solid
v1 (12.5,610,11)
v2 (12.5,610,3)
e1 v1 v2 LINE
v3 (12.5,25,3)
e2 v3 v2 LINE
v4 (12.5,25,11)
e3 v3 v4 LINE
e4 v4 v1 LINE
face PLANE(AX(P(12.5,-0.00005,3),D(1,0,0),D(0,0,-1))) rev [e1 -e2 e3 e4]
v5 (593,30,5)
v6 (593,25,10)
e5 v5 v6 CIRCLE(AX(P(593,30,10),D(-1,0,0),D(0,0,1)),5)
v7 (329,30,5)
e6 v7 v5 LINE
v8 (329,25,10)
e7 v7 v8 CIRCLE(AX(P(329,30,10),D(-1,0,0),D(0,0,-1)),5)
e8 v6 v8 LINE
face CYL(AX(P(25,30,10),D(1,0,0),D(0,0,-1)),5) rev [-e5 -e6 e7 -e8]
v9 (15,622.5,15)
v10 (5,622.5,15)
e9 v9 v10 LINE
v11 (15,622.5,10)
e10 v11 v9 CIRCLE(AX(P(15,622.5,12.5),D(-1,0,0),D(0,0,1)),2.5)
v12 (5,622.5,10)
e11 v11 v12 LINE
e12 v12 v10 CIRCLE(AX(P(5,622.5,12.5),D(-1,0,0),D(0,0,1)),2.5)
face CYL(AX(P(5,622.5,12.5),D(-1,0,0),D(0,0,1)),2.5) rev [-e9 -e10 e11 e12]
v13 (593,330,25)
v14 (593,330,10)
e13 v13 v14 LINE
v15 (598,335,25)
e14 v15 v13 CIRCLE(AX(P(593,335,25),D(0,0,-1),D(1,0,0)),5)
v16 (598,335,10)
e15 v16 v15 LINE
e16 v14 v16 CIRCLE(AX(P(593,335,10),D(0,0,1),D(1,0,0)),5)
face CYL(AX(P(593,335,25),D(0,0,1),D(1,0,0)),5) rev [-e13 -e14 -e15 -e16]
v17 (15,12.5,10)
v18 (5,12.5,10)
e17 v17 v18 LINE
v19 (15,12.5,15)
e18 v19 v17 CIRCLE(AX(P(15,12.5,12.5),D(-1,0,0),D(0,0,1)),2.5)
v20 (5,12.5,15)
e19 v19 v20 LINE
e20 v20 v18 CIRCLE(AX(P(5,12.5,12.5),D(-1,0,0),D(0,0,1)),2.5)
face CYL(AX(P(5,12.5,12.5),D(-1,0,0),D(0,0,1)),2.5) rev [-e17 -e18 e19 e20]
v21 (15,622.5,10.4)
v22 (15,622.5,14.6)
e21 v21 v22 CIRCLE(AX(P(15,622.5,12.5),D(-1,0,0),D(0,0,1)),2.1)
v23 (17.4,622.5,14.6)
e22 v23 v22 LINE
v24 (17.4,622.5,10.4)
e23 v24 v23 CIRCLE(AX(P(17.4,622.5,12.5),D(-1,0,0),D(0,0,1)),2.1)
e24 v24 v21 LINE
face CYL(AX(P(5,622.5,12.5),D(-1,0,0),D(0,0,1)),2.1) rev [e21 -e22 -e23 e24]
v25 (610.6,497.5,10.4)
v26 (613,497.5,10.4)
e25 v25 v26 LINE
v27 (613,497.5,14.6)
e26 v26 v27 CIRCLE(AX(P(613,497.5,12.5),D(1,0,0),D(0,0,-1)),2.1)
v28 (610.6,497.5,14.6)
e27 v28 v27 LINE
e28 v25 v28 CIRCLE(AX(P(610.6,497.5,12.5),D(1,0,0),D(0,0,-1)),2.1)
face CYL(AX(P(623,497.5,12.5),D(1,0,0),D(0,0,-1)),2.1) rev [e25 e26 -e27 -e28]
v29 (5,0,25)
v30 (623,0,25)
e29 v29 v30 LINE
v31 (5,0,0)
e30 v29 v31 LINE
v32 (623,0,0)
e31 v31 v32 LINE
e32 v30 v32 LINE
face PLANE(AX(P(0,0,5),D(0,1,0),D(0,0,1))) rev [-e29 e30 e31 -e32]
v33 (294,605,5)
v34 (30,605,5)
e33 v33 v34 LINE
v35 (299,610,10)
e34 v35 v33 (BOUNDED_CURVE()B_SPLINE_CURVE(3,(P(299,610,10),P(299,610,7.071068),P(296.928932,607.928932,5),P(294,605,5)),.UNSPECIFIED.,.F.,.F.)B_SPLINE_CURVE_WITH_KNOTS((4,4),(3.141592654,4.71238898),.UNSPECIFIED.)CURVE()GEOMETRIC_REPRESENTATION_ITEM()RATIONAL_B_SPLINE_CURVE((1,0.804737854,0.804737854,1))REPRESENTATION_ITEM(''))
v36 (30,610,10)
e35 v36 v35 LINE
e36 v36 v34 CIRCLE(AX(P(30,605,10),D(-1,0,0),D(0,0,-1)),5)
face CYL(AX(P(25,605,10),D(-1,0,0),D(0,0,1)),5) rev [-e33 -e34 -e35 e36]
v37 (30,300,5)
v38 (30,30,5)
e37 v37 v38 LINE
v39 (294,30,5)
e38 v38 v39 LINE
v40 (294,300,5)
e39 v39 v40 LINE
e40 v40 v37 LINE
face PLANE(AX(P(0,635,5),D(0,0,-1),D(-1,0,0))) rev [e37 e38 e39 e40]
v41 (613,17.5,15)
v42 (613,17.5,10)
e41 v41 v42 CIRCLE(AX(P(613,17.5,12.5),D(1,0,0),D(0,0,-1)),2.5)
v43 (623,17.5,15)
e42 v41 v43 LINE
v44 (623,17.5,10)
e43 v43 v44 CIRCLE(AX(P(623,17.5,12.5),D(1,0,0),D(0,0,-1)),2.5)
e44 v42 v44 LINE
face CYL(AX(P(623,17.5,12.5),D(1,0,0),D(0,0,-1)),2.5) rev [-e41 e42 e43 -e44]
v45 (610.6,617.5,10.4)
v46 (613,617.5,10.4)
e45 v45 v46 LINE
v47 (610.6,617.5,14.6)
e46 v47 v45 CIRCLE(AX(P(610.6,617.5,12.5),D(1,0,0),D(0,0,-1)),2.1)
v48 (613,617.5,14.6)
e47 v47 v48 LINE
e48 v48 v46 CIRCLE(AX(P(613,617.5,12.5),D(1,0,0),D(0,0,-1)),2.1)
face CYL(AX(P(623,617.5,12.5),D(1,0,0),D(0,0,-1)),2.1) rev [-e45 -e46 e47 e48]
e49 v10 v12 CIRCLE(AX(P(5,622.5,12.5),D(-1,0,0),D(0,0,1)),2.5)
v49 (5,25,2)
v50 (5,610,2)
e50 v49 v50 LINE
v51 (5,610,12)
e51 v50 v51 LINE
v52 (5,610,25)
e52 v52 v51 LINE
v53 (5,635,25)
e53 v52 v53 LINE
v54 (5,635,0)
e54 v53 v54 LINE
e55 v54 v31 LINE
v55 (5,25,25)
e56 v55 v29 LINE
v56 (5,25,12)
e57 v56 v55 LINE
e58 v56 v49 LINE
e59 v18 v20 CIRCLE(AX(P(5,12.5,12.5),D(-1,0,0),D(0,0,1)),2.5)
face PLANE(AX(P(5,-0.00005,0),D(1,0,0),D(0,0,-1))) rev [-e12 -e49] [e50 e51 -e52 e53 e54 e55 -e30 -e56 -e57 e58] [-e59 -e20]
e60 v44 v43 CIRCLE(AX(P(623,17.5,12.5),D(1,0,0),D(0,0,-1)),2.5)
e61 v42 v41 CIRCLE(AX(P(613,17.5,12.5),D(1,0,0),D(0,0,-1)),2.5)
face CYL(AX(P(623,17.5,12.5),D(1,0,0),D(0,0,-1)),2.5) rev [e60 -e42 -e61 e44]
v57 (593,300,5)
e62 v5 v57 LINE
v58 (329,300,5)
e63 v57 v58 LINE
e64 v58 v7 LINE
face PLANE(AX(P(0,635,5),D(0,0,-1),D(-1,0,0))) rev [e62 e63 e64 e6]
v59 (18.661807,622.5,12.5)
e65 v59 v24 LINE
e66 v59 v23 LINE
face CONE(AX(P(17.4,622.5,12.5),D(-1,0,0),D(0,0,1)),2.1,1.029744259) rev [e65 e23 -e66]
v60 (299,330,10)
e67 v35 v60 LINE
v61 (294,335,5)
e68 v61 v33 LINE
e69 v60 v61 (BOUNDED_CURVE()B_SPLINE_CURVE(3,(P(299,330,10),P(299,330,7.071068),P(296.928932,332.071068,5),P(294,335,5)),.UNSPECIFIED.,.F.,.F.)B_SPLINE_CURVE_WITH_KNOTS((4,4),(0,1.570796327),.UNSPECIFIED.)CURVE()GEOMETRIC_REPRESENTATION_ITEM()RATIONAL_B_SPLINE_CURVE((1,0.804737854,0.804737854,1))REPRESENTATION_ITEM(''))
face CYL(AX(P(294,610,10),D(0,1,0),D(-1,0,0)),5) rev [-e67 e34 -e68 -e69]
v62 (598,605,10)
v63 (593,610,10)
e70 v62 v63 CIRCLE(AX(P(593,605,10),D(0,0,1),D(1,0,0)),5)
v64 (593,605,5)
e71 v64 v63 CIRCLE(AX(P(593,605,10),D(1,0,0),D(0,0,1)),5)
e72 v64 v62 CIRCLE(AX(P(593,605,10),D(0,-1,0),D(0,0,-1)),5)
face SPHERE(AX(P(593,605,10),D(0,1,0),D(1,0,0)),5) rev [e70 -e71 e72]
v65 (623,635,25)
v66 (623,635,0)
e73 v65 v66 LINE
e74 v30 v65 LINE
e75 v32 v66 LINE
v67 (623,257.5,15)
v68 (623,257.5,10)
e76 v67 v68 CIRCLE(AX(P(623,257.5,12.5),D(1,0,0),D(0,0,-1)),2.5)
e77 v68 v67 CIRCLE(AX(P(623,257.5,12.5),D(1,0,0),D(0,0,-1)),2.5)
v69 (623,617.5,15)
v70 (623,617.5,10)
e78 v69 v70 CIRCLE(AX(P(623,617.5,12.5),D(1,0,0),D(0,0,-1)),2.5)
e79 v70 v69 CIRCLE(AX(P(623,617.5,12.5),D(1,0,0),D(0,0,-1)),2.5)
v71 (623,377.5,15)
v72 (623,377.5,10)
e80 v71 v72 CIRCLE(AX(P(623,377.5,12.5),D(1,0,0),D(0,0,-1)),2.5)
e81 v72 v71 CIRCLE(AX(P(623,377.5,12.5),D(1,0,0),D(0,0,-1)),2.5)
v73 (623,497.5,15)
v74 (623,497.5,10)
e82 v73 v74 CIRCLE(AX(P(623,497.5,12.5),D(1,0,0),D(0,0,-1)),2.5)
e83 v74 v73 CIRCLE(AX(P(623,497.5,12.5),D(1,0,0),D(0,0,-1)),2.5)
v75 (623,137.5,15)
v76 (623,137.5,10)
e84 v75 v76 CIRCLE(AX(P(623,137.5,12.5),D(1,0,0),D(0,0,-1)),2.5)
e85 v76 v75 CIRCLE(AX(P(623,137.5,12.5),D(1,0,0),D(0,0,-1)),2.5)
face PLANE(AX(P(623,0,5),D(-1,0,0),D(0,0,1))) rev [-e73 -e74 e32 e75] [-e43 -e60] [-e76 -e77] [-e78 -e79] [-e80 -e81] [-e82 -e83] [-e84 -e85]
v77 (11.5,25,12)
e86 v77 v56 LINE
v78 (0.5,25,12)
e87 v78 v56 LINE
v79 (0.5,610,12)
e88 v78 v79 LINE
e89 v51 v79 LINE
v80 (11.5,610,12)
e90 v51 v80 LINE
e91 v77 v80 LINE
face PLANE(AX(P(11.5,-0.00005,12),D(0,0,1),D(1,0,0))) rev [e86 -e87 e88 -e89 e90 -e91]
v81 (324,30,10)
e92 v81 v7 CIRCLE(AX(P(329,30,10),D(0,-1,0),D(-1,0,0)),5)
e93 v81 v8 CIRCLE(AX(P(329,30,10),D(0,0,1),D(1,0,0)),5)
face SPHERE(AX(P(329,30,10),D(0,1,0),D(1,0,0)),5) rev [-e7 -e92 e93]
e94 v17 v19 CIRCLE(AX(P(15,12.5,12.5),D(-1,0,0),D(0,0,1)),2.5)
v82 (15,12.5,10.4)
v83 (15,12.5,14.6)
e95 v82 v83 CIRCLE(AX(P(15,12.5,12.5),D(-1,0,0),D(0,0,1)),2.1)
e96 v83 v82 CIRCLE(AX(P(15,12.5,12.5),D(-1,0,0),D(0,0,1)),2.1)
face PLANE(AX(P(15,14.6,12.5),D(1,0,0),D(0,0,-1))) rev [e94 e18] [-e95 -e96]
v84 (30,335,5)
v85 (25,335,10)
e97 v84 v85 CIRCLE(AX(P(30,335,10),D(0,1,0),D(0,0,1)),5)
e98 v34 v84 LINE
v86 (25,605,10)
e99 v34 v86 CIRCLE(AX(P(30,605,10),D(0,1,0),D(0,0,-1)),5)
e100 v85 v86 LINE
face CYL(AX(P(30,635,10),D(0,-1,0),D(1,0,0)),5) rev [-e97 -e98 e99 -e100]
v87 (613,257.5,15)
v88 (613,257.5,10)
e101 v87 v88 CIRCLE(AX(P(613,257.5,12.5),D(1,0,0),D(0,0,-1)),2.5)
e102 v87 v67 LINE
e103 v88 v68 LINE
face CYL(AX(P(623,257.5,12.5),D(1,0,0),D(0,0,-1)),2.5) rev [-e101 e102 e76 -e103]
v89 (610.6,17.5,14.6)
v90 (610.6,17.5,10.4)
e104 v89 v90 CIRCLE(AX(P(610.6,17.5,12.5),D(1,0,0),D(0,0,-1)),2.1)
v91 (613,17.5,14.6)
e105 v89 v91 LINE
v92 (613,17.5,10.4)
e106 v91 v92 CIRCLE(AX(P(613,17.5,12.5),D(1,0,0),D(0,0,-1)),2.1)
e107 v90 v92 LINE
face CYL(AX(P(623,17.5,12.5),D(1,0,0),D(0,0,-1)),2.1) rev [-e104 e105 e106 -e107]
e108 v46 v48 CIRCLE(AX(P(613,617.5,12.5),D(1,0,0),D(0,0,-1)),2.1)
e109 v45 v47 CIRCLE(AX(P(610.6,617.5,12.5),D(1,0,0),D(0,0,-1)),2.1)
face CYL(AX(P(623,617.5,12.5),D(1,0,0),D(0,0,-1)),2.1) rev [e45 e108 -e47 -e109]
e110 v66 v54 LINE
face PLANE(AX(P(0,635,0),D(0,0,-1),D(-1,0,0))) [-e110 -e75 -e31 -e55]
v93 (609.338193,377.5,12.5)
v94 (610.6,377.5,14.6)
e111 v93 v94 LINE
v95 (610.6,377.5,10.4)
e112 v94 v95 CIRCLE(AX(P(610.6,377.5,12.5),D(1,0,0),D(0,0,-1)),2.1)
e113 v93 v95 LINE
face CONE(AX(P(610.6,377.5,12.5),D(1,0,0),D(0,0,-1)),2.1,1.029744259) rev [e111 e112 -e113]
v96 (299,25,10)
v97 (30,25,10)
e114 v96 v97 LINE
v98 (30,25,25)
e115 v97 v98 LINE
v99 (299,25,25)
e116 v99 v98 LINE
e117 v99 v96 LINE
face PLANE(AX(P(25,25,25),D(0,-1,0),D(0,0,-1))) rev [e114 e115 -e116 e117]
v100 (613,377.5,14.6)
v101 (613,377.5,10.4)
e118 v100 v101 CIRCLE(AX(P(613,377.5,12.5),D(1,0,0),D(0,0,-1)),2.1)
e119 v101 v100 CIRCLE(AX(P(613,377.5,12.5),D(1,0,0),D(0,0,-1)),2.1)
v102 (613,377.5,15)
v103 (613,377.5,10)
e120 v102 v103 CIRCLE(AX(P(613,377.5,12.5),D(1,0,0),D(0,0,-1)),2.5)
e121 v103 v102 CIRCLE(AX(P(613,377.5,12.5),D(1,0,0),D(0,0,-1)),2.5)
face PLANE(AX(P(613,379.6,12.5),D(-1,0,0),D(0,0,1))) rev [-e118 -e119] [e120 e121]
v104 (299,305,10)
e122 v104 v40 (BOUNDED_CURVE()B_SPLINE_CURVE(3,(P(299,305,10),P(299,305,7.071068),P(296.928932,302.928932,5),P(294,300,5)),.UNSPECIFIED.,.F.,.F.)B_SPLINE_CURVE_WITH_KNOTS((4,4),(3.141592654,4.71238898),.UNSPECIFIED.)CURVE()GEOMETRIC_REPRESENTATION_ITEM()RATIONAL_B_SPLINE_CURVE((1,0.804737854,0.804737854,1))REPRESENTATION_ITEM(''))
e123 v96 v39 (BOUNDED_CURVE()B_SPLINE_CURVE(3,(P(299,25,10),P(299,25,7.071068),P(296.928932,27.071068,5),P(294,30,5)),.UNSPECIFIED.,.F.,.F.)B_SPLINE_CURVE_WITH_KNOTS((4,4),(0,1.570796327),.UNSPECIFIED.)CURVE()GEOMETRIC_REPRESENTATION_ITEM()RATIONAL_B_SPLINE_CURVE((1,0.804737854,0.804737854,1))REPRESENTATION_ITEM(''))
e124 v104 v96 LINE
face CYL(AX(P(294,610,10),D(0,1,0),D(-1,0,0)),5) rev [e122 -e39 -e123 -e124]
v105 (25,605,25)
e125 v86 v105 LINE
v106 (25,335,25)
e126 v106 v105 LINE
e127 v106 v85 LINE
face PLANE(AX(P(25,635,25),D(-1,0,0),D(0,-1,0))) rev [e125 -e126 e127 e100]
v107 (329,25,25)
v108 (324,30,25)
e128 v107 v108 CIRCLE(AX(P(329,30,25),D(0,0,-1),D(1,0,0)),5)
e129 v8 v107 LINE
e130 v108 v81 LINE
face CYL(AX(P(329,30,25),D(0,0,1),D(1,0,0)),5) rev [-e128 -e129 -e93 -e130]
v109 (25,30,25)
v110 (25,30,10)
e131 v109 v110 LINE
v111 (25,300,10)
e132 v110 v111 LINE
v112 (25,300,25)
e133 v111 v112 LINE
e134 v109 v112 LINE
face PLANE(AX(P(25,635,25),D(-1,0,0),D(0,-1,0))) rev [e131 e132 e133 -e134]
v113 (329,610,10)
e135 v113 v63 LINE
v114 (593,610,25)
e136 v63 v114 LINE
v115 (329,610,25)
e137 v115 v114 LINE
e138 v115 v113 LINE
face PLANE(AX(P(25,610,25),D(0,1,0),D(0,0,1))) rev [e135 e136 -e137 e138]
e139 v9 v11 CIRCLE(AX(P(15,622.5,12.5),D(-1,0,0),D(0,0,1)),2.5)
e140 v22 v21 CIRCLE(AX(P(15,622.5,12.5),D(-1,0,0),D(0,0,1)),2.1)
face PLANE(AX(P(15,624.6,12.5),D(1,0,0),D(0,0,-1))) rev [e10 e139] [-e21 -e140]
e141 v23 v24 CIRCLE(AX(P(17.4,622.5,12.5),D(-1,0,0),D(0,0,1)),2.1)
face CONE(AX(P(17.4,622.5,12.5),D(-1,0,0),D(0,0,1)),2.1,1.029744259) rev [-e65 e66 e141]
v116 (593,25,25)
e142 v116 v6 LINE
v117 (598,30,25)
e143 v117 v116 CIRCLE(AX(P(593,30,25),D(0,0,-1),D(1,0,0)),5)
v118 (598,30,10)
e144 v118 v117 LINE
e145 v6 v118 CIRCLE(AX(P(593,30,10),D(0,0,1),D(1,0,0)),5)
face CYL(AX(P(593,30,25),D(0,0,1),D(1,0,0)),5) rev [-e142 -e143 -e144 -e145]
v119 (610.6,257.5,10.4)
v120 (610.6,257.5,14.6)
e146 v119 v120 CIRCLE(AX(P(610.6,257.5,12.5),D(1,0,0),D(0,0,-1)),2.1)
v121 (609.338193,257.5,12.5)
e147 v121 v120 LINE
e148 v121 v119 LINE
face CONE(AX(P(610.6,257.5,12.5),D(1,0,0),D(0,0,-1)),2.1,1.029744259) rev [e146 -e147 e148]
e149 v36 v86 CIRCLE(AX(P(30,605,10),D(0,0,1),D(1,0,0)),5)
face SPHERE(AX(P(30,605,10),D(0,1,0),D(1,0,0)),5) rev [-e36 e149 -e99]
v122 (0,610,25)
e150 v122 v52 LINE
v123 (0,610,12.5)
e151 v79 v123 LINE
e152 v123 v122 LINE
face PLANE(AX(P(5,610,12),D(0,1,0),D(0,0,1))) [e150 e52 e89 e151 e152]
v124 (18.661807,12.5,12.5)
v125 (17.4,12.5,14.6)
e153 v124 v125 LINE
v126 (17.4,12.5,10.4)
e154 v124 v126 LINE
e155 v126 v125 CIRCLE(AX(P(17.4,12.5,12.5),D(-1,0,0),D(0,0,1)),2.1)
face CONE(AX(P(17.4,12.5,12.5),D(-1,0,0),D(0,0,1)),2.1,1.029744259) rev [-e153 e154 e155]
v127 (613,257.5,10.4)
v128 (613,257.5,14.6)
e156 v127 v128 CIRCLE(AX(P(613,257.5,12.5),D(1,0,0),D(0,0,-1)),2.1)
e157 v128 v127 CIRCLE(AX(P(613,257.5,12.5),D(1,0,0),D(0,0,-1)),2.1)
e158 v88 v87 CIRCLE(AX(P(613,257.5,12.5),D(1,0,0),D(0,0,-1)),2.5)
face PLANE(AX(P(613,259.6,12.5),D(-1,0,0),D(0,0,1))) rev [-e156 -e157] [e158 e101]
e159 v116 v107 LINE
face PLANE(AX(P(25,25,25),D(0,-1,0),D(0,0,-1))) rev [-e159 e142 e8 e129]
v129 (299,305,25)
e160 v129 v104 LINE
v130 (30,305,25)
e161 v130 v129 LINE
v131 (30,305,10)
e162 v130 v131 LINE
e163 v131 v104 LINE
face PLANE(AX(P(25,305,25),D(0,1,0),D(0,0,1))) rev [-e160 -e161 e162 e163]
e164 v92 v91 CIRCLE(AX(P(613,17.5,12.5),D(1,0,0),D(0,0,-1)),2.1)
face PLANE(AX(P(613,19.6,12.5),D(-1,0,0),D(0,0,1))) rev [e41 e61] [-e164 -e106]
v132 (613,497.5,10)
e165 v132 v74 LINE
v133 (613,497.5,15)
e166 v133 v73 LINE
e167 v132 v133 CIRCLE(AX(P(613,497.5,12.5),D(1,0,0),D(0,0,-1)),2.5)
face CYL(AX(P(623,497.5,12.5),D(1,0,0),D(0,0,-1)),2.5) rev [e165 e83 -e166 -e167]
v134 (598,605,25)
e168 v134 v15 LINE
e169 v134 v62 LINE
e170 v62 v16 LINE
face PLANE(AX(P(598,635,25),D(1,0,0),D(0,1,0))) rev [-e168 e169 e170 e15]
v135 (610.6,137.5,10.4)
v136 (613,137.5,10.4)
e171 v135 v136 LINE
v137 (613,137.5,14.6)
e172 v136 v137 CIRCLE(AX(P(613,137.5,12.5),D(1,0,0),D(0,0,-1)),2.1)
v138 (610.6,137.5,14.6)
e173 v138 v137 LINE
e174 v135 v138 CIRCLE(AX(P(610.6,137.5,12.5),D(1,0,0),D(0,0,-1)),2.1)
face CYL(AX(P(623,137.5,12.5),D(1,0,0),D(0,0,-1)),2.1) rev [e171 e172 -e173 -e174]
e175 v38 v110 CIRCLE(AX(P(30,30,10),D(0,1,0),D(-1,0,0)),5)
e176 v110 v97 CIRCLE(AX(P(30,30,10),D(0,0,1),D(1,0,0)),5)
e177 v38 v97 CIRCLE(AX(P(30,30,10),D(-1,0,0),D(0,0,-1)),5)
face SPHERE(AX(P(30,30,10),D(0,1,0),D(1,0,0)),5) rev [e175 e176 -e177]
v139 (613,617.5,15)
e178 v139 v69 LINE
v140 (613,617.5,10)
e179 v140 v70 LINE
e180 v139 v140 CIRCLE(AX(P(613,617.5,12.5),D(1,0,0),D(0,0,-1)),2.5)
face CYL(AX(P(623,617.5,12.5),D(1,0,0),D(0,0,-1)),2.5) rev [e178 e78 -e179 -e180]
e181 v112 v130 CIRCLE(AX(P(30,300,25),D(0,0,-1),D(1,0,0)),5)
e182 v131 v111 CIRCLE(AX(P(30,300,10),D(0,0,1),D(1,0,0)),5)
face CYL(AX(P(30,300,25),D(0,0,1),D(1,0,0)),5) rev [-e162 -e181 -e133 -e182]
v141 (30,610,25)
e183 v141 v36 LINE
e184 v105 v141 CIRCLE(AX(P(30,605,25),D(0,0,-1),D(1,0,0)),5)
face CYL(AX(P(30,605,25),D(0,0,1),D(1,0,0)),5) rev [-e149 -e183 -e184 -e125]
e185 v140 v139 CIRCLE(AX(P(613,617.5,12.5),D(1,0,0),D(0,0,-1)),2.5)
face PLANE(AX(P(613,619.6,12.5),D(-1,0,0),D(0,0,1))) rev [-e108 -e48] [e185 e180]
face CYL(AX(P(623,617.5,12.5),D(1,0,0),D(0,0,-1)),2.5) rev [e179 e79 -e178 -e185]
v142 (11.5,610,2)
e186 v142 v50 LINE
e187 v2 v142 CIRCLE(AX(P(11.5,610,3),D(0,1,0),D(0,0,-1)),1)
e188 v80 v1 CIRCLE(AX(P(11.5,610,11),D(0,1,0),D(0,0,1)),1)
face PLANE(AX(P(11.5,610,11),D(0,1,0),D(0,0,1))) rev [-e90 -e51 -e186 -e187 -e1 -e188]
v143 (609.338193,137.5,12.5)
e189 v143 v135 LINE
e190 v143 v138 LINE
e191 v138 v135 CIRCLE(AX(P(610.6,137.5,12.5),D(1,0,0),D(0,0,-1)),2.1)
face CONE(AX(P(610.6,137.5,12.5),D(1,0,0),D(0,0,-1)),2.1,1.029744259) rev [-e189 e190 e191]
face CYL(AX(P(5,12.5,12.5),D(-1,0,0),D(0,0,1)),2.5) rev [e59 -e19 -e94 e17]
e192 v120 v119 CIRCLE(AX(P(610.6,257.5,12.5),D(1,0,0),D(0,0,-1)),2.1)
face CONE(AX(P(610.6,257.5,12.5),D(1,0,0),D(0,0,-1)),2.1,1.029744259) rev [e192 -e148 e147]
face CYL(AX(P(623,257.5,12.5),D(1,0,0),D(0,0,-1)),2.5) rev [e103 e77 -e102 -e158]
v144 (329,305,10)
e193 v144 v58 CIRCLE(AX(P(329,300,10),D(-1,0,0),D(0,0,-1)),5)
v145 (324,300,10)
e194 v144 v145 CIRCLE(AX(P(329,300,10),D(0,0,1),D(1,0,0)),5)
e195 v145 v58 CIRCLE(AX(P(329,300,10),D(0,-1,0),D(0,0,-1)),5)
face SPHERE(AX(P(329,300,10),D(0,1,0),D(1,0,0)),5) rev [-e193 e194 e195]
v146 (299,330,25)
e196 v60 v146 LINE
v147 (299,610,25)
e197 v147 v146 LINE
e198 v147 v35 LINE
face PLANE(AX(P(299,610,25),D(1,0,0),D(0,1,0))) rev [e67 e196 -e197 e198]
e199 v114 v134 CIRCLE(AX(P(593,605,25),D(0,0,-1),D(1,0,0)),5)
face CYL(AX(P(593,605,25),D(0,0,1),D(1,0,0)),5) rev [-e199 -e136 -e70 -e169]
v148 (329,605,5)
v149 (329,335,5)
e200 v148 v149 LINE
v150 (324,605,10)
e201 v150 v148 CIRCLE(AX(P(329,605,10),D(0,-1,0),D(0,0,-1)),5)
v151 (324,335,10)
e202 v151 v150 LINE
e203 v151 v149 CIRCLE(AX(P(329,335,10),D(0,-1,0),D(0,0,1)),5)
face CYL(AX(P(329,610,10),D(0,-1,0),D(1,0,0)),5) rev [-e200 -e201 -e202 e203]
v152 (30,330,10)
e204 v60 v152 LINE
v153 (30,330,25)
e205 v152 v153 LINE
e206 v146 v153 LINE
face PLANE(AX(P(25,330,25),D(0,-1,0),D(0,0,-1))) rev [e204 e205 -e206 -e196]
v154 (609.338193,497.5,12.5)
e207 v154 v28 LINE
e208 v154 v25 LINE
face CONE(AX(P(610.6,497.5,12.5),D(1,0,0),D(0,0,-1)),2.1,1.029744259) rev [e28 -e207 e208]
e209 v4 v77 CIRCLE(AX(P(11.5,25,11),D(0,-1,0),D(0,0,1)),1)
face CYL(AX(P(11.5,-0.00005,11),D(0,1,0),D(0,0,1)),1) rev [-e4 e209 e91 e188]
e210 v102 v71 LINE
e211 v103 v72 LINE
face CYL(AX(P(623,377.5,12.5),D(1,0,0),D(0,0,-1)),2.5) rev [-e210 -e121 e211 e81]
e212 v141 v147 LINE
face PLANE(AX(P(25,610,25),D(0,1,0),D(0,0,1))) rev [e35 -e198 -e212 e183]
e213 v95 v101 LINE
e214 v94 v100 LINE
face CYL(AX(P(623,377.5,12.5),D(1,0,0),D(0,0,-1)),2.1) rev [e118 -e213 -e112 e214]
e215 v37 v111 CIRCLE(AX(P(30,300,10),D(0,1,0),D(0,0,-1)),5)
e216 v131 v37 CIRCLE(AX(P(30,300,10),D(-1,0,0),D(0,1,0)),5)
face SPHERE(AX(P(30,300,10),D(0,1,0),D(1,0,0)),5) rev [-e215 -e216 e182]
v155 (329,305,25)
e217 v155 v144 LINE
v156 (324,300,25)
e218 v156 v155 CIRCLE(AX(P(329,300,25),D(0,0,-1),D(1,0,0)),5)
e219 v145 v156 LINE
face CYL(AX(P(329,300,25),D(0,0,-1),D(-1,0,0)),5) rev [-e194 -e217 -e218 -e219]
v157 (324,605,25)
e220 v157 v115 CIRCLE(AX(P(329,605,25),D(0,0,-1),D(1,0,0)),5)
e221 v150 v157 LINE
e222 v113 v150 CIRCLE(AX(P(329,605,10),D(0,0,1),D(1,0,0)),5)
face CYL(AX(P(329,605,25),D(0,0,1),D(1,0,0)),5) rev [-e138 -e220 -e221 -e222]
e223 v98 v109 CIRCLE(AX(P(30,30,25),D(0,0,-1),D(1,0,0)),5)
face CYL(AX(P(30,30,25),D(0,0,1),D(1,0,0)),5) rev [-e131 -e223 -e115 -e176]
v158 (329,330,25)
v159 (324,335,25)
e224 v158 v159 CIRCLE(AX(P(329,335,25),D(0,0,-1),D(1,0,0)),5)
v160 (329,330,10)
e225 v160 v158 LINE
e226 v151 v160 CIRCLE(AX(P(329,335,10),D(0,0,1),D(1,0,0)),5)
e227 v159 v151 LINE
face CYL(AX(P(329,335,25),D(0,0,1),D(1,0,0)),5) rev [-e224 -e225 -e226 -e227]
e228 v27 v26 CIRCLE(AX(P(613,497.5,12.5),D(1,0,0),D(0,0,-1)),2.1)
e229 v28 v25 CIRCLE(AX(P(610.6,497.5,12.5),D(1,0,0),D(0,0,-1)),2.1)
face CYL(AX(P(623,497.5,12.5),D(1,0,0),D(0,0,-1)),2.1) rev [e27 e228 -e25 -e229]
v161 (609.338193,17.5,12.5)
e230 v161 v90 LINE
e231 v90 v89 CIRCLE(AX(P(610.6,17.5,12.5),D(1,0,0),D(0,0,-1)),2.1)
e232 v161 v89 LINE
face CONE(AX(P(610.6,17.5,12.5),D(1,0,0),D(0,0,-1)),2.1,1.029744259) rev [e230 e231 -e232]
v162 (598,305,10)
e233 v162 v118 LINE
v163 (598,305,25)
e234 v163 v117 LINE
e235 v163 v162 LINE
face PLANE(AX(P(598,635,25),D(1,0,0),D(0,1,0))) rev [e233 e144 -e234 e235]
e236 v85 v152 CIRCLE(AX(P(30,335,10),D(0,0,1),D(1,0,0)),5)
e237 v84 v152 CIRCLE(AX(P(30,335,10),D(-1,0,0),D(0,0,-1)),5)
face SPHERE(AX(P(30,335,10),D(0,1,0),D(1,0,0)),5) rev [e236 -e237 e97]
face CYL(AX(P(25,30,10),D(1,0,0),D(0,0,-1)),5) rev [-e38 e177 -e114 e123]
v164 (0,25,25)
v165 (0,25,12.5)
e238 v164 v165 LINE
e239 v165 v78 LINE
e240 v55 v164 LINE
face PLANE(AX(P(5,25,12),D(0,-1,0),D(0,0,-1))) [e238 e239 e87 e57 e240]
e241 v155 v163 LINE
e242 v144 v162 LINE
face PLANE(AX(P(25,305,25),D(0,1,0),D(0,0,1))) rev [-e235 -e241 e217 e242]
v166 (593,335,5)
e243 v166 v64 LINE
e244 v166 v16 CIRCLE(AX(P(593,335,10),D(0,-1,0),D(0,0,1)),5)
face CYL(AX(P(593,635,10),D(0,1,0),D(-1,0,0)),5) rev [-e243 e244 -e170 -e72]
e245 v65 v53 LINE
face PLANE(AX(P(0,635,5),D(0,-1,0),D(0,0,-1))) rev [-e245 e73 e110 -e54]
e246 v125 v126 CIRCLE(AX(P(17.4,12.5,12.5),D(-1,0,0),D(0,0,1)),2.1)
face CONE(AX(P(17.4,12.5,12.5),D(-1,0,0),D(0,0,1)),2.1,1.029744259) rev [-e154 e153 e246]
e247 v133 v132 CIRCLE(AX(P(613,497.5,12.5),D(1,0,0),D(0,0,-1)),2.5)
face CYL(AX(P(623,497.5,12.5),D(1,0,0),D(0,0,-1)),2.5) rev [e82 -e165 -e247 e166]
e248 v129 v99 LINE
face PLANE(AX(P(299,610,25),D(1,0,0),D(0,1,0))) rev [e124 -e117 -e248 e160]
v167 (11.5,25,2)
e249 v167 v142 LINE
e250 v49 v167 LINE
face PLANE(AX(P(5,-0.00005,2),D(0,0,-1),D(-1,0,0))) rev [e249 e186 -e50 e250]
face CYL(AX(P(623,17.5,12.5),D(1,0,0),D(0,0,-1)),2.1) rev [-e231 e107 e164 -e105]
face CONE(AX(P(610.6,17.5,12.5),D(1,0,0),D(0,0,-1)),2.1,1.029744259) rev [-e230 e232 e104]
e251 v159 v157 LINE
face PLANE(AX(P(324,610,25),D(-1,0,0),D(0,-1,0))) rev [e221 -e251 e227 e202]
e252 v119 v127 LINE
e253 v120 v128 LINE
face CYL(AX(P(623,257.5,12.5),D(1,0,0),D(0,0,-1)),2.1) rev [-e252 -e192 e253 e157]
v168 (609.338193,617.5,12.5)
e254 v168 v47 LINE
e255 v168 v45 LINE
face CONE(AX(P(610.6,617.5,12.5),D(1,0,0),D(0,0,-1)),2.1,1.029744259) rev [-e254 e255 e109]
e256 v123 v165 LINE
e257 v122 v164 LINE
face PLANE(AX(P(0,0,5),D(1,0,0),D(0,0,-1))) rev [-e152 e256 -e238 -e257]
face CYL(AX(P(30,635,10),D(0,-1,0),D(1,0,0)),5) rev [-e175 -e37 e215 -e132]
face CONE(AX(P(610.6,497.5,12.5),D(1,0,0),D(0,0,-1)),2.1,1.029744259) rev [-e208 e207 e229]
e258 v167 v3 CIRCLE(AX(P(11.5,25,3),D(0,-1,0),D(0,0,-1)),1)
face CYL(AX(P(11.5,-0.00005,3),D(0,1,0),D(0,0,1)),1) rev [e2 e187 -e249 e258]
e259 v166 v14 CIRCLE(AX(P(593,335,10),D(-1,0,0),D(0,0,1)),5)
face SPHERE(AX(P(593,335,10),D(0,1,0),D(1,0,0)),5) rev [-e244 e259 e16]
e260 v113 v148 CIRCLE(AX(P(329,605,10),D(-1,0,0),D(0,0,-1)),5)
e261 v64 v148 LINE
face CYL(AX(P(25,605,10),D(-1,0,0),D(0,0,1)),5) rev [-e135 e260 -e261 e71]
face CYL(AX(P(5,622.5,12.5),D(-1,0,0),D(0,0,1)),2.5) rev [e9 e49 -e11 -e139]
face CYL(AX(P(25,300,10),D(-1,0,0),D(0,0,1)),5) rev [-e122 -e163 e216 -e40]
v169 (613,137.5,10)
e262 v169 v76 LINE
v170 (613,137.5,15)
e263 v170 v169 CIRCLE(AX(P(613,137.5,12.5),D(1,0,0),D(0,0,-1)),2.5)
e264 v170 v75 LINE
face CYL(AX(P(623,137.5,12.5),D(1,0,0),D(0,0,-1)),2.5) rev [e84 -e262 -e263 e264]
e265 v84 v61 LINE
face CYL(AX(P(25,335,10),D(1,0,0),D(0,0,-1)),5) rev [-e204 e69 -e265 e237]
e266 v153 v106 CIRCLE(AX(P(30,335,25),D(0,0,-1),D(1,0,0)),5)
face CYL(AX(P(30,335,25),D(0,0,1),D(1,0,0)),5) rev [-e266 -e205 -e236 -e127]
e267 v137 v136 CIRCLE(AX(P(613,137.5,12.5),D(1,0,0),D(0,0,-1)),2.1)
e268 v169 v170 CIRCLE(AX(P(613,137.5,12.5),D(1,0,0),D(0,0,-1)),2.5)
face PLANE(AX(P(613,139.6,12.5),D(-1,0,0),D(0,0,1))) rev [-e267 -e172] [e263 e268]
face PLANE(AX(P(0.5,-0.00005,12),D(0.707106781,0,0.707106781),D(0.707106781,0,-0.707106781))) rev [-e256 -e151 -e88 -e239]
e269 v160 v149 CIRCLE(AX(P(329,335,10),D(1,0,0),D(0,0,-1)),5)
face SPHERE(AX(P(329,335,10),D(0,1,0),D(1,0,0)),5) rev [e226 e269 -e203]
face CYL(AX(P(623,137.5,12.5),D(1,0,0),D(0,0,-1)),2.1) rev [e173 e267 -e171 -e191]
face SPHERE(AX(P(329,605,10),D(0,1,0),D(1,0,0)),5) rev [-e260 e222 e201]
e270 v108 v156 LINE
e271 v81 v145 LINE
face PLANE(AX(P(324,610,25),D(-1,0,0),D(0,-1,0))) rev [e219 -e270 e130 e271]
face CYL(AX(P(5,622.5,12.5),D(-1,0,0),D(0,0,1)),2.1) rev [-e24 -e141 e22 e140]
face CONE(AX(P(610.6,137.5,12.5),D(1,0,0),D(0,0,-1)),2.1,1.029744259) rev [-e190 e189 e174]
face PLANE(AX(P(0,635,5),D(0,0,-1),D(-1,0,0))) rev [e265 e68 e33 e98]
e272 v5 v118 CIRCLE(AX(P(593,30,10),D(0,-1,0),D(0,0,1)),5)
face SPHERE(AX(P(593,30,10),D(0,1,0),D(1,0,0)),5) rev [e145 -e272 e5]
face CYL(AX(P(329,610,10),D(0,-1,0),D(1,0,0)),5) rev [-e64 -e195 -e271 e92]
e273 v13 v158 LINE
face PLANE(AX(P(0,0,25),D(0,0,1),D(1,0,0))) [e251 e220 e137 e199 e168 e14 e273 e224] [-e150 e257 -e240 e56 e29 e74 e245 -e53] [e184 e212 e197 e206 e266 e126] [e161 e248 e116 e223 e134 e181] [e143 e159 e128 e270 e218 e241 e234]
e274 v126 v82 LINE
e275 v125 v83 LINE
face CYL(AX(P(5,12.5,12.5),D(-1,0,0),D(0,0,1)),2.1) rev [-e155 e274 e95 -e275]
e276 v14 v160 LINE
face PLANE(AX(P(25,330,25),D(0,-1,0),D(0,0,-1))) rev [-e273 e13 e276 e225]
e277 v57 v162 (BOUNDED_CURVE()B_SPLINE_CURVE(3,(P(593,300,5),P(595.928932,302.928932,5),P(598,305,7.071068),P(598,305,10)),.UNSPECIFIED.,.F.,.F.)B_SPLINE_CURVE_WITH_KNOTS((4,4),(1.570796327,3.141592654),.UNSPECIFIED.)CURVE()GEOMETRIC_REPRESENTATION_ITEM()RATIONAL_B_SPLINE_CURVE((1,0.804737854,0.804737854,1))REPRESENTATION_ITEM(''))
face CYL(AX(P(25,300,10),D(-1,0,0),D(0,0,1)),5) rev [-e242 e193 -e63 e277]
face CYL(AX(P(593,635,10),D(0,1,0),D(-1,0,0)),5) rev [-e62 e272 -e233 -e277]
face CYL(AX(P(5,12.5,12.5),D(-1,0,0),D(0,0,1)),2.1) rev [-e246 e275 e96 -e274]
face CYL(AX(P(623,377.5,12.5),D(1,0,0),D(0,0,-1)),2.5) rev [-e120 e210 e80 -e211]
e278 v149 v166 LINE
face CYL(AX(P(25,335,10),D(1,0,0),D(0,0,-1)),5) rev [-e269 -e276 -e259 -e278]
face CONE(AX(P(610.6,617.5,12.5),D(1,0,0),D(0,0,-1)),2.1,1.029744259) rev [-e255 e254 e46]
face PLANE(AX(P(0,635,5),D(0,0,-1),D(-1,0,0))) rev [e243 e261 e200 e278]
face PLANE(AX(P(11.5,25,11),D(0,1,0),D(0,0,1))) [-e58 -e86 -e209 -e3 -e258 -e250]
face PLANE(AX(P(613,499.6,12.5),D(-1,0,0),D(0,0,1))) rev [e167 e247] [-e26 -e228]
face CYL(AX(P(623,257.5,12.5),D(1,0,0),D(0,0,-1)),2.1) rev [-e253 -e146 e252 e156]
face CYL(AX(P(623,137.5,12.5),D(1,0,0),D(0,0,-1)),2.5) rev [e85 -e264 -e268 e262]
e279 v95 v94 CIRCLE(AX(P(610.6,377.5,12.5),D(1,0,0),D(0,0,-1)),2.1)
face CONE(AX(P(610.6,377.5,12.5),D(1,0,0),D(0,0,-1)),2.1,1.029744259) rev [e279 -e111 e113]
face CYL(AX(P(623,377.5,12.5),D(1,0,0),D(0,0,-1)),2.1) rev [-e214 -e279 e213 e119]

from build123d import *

# Parameters (mm, degrees)
SKETCH_1_W           = 623
SKETCH_1_H           = 635
EXTRUDE_1_DEPTH      = 5
SKETCH_2_W           = 25
SKETCH_2_H           = 635
EXTRUDE_2_DEPTH      = 20
SKETCH_3_W           = 25
SKETCH_3_H           = 635
EXTRUDE_3_DEPTH      = 20
CUT_EXTRUDE_1_DEPTH  = 890.932019876
CHAMFER_1_SIZE       = 0.5
SKETCH_7_W           = 573
SKETCH_7_H           = 25
EXTRUDE_4_DEPTH      = 20
SKETCH_8_W           = 573
SKETCH_8_H           = 25
EXTRUDE_5_DEPTH      = 20
SKETCH_9_W           = 573
SKETCH_9_H           = 25
EXTRUDE_6_DEPTH      = 20
SKETCH_10_W          = 25
SKETCH_10_H          = 585
EXTRUDE_7_DEPTH      = 20
EXTRUDE_8_DEPTH      = 25
CUT_EXTRUDE_2_DEPTH  = 25
EXTRUDE_START        = -25
EXTRUDE_9_DEPTH      = 25
CUT_EXTRUDE_3_DEPTH  = 25
M5X0_8_1_D           = 4.2
M5X0_8_1_DEPTH       = 12.4
M5X0_8_1_CBORE_D     = 5
M5X0_8_1_CBORE_DEPTH = 10
M5X0_8_1_TIP         = 1.2618073
M5X0_8_2_D           = 4.2
M5X0_8_2_DEPTH       = 12.4
M5X0_8_2_CBORE_D     = 5
M5X0_8_2_CBORE_DEPTH = 10
M5X0_8_2_TIP         = 1.2618073
FILLET_1_R           = 5


with BuildPart() as part:
    # 草图1 → 拉伸1 (new body)
    with BuildSketch(Plane.XY):
        with Locations((311.5, 317.5)):
            Rectangle(SKETCH_1_W, SKETCH_1_H)
    extrude(amount=EXTRUDE_1_DEPTH)

    # 草图2 → 拉伸2 (add)
    with BuildSketch(Plane.XY.offset(5)):
        with Locations((12.5, 317.5)):
            Rectangle(SKETCH_2_W, SKETCH_2_H)
    extrude(amount=EXTRUDE_2_DEPTH)

    # 草图3 → 拉伸3 (add)
    with BuildSketch(Plane.XY.offset(5)):
        with Locations((610.5, 317.5)):
            Rectangle(SKETCH_3_W, SKETCH_3_H)
    extrude(amount=EXTRUDE_3_DEPTH)

    # 草图4 → 切除-拉伸1 (cut, through all)
    with BuildSketch(Plane(origin=(0, 635, 0), x_dir=(-1, 0, 0), z_dir=(0, 1, 0))):
        with BuildLine():
            Line((0, 0), (-5, 0))
            Line((-5, 0), (-5, 2))
            Line((-5, 2), (-11.5, 2))
            ThreePointArc((-11.5, 2), (-12.207106781, 2.292893219), (-12.5, 3))
            Line((-12.5, 3), (-12.5, 11))
            ThreePointArc((-12.5, 11), (-12.207106781, 11.707106781), (-11.5, 12))
            Line((-11.5, 12), (0, 12))
            Line((0, 12), (0, 0))
        make_face()
    extrude(amount=-CUT_EXTRUDE_1_DEPTH, mode=Mode.SUBTRACT)

    # 倒角1
    chamfer_1_edges = [part.edges().sort_by_distance(p)[0] for p in [
        (0, 317.5, 12),
    ]]
    chamfer(chamfer_1_edges, length=CHAMFER_1_SIZE)

    # 草图7 → 拉伸4 (add)
    with BuildSketch(Plane.XY.offset(5)):
        with Locations((311.5, 622.5)):
            Rectangle(SKETCH_7_W, SKETCH_7_H)
    extrude(amount=EXTRUDE_4_DEPTH)

    # 草图8 → 拉伸5 (add)
    with BuildSketch(Plane.XY.offset(5)):
        with Locations((311.5, 12.5)):
            Rectangle(SKETCH_8_W, SKETCH_8_H)
    extrude(amount=EXTRUDE_5_DEPTH)

    # 草图9 → 拉伸6 (add)
    with BuildSketch(Plane.XY.offset(5)):
        with Locations((311.5, 317.5)):
            Rectangle(SKETCH_9_W, SKETCH_9_H)
    extrude(amount=EXTRUDE_6_DEPTH)

    # 草图10 → 拉伸7 (add)
    with BuildSketch(Plane.XY.offset(5)):
        with Locations((311.5, 317.5)):
            Rectangle(SKETCH_10_W, SKETCH_10_H)
    extrude(amount=EXTRUDE_7_DEPTH)

    # 草图11 → 拉伸8 (add)
    with BuildSketch(Plane(origin=(0, 635, 0), x_dir=(-1, 0, 0), z_dir=(0, 1, 0))):
        with BuildLine():
            Line((-5, 2), (-5, 12))
            Line((-5, 12), (-11.5, 12))
            ThreePointArc((-11.5, 12), (-12.207106781, 11.707106781), (-12.5, 11))
            Line((-12.5, 11), (-12.5, 3))
            ThreePointArc((-12.5, 3), (-12.207106781, 2.292893219), (-11.5, 2))
            Line((-11.5, 2), (-5, 2))
        make_face()
    extrude(amount=-EXTRUDE_8_DEPTH)

    # 草图12 → 切除-拉伸2 (cut)
    with BuildSketch(Plane(origin=(0, 635, 0), x_dir=(-1, 0, 0), z_dir=(0, 1, 0))):
        Polygon((-5, 12), (-0.5, 12), (0, 12.5), (0, 25), (-5, 25), align=None)
    extrude(amount=-CUT_EXTRUDE_2_DEPTH, mode=Mode.SUBTRACT)

    # 草图13 → 拉伸9 (add)
    with BuildSketch(Plane.XZ.offset(EXTRUDE_START)):
        with BuildLine():
            Line((5, 2), (5, 12))
            Line((5, 12), (11.5, 12))
            ThreePointArc((11.5, 12), (12.207106781, 11.707106781), (12.5, 11))
            Line((12.5, 11), (12.5, 3))
            ThreePointArc((12.5, 3), (12.207106781, 2.292893219), (11.5, 2))
            Line((11.5, 2), (5, 2))
        make_face()
    extrude(amount=EXTRUDE_9_DEPTH)

    # 草图14 → 切除-拉伸3 (cut)
    with BuildSketch(Plane.XZ):
        Polygon((5, 12), (5, 25), (0, 25), (0, 12.5), (0.5, 12), align=None)
    extrude(amount=-CUT_EXTRUDE_3_DEPTH, mode=Mode.SUBTRACT)

    # M5x0.8 螺纹孔1
    with Locations(Plane(origin=(623, 617.5, 12.5), x_dir=(0, 0, 1), z_dir=(1, 0, 0))):
        with Locations((0, 0), (0, 120), (0, 240), (0, 360), (0, 480), (0, 600)):
            CounterBoreHole(M5X0_8_1_D / 2, M5X0_8_1_CBORE_D / 2, M5X0_8_1_CBORE_DEPTH, depth=M5X0_8_1_DEPTH)
            with Locations((0, 0, -(M5X0_8_1_DEPTH + M5X0_8_1_TIP / 2))):  # 118° drill point
                Cone(0, M5X0_8_1_D / 2, M5X0_8_1_TIP, mode=Mode.SUBTRACT)

    # M5x0.8 螺纹孔2
    with Locations(Plane(origin=(5, 12.5, 12.5), x_dir=(0, 0, -1), z_dir=(-1, 0, 0))):
        with Locations((0, 0), (0, -610)):
            CounterBoreHole(M5X0_8_2_D / 2, M5X0_8_2_CBORE_D / 2, M5X0_8_2_CBORE_DEPTH, depth=M5X0_8_2_DEPTH)
            with Locations((0, 0, -(M5X0_8_2_DEPTH + M5X0_8_2_TIP / 2))):  # 118° drill point
                Cone(0, M5X0_8_2_D / 2, M5X0_8_2_TIP, mode=Mode.SUBTRACT)

    # 圆角1
    fillet_1_edges = [part.edges().sort_by_distance(p)[0] for p in [
        (461, 25, 5),
        (598, 25, 15),
        (598, 165, 5),
        (25, 470, 5),
        (25, 330, 15),
        (162, 305, 5),
        (25, 305, 15),
        (461, 330, 5),
        (598, 330, 15),
        (162, 330, 5),
        (324, 330, 15),
        (461, 305, 5),
        (162, 25, 5),
        (461, 610, 5),
        (299, 165, 5),
        (299, 470, 5),
        (324, 165, 5),
        (324, 305, 15),
        (324, 25, 15),
        (324, 470, 5),
        (324, 610, 15),
        (598, 470, 5),
        (162, 610, 5),
        (25, 610, 15),
        (598, 610, 15),
        (25, 165, 5),
        (25, 25, 15),
    ]]
    fillet(fillet_1_edges, radius=FILLET_1_R)


solid = part.part
